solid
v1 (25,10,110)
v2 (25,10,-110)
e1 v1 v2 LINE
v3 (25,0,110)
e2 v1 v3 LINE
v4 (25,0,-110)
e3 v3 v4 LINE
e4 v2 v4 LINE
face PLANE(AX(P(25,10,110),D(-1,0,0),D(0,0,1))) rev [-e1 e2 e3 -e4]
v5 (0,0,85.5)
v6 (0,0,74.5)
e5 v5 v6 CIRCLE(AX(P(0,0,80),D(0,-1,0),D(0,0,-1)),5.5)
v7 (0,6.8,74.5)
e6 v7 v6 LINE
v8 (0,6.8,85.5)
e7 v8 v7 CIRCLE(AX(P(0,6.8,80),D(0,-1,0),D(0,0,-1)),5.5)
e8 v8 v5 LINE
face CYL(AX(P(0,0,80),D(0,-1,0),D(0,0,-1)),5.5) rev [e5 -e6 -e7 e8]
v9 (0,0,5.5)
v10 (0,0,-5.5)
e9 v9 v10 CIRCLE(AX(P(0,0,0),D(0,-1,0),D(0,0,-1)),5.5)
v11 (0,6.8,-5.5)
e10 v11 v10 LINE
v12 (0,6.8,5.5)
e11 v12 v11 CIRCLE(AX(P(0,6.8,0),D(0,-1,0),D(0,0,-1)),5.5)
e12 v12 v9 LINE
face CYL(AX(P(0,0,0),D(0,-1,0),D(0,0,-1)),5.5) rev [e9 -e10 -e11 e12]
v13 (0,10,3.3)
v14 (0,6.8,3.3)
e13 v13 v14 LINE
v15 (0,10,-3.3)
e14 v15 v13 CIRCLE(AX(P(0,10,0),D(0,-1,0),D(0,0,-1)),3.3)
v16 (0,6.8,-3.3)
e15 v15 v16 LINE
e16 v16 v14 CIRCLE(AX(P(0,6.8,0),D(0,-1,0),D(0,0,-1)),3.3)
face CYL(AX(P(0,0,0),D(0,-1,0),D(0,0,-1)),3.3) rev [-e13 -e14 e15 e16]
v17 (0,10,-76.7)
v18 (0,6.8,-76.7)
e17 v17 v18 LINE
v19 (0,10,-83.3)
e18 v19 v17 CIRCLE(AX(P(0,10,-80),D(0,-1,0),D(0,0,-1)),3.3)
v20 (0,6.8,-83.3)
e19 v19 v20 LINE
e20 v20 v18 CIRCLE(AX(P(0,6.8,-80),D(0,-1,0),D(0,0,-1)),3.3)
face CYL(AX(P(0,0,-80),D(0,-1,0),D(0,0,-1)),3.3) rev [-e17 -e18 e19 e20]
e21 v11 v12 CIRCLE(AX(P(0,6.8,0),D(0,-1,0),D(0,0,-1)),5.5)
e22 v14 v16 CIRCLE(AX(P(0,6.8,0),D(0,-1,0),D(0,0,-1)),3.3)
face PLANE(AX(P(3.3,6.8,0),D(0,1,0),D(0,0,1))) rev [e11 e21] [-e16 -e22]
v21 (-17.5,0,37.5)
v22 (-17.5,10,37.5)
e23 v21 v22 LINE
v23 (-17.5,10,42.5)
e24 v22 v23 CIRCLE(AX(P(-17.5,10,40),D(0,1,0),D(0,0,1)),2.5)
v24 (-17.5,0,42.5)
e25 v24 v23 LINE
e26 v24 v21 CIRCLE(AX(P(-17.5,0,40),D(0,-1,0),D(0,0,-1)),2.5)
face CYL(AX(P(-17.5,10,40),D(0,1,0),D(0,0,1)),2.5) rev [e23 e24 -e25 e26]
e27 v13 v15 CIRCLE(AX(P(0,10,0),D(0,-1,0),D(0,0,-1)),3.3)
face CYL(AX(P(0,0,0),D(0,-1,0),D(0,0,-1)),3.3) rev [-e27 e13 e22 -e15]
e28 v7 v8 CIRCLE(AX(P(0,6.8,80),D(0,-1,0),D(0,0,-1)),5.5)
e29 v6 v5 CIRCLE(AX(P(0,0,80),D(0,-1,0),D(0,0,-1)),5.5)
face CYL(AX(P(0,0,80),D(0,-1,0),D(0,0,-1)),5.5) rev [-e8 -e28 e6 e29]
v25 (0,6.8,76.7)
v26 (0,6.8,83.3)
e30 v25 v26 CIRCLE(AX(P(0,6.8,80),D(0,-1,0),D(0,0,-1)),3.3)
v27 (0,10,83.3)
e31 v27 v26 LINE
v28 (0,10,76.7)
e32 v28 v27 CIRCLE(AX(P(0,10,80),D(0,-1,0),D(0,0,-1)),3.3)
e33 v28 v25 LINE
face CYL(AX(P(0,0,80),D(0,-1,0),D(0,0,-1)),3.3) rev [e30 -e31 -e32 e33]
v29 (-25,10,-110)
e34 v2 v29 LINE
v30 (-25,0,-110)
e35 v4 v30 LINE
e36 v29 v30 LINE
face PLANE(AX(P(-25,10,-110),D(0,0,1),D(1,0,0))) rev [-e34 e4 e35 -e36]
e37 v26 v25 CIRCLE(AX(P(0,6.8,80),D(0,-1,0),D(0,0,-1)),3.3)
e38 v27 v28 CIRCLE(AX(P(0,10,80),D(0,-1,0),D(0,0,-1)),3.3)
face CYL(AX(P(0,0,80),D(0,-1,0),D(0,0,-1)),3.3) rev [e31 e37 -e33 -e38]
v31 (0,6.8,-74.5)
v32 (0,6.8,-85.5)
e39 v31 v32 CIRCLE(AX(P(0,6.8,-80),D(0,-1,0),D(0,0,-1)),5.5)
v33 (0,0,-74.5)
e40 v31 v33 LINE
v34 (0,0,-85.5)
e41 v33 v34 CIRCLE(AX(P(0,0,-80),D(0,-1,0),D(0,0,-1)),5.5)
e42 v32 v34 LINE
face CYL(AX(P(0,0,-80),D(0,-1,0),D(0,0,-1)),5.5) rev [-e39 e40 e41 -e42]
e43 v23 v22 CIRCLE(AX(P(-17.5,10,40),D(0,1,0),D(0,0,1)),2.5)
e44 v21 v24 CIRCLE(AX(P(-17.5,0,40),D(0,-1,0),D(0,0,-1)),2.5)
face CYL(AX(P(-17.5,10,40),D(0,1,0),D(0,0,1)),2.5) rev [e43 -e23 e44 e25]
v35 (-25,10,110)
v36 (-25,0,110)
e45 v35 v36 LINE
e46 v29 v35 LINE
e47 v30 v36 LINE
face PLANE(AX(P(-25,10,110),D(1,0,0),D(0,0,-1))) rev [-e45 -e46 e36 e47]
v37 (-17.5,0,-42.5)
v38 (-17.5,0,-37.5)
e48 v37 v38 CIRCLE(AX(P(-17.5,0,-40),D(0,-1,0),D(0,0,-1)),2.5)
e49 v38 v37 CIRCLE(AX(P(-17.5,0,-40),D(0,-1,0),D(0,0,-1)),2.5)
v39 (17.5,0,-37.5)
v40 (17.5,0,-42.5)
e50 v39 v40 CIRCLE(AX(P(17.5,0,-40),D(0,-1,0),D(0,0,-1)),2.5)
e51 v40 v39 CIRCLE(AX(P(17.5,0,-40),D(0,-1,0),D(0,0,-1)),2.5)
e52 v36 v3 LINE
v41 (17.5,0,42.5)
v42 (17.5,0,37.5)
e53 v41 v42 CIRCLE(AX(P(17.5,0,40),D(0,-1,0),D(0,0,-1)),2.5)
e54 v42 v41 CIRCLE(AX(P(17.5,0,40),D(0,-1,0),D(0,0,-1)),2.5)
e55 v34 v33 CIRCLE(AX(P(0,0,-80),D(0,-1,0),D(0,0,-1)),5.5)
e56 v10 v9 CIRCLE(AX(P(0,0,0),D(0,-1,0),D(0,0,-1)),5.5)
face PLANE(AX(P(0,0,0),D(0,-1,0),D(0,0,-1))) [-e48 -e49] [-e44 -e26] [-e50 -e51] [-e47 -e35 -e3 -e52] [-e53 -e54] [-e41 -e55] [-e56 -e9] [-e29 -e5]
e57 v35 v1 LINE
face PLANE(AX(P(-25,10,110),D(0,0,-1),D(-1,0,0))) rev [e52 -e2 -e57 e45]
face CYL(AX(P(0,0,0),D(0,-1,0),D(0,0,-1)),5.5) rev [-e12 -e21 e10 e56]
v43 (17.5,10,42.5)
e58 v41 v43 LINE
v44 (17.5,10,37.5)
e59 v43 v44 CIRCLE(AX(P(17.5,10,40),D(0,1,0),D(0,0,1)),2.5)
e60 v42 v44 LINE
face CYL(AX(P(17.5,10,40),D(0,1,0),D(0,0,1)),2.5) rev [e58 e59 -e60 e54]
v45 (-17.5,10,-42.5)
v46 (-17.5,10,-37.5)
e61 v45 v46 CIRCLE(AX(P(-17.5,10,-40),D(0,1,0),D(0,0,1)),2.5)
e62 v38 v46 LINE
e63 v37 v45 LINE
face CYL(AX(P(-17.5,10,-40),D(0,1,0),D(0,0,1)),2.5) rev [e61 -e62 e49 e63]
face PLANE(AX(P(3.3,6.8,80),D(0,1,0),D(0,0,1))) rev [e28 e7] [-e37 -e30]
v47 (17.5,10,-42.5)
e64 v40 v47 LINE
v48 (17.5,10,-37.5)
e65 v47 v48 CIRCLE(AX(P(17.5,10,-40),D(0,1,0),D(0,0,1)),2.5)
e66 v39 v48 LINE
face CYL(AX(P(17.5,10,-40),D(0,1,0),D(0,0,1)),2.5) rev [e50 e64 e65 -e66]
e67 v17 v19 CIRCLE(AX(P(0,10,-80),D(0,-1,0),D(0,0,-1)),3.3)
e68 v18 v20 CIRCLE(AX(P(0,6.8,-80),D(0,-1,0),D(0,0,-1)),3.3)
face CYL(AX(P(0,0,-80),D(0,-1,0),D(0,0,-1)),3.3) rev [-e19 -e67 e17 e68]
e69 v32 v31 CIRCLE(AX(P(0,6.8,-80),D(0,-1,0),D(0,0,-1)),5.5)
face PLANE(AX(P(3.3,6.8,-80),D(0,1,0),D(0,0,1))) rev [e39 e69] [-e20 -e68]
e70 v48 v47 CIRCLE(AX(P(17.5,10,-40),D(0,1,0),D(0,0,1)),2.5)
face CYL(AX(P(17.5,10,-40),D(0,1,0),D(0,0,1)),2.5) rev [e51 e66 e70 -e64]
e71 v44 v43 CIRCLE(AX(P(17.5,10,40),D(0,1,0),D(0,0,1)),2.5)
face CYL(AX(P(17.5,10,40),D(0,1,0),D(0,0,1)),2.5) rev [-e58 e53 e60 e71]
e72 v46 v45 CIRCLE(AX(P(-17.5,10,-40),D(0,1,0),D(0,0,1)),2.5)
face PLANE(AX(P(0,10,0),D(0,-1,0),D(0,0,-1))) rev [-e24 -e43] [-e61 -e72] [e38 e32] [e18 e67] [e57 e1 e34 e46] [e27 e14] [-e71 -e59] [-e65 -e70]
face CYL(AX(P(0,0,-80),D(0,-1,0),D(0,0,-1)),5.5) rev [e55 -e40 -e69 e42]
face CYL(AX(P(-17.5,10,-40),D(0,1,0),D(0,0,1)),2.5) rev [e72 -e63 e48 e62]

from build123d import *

# Parameters (mm, degrees)
SKETCH1_W                                         = 50
SKETCH1_H                                         = 220
BOSS_EXTRUDE1_DEPTH                               = 10
HOLE_SIZE_BY_SOCKET_HEAD_CAP_SCREW_TY_D           = 6.6
HOLE_SIZE_BY_SOCKET_HEAD_CAP_SCREW_TY_CBORE_D     = 11
HOLE_SIZE_BY_SOCKET_HEAD_CAP_SCREW_TY_CBORE_DEPTH = 6.8
M6_TAPPED_HOLE1_D                                 = 5
M6_TAPPED_HOLE1_DEPTH                             = 15
M6_TAPPED_HOLE1_TIP                               = 1.502151548


with BuildPart() as part:
    # Sketch1 → Boss-Extrude1 (new body)
    with BuildSketch(Plane(origin=(0, 0, 0), x_dir=(1, 0, 0), z_dir=(0, 1, 0))):
        Rectangle(SKETCH1_W, SKETCH1_H)
    extrude(amount=BOSS_EXTRUDE1_DEPTH)

    # Hole Size (% by) Socket Head Cap Screw Type1 (through all)
    with Locations(Plane(origin=(0, 0, 0), x_dir=(-1, 0, 0), z_dir=(0, -1, 0))):
        with Locations((0, -80), (0, 80), (0, 0)):
            CounterBoreHole(HOLE_SIZE_BY_SOCKET_HEAD_CAP_SCREW_TY_D / 2, HOLE_SIZE_BY_SOCKET_HEAD_CAP_SCREW_TY_CBORE_D / 2, HOLE_SIZE_BY_SOCKET_HEAD_CAP_SCREW_TY_CBORE_DEPTH)

    # M6 Tapped Hole1
    with Locations(Plane(origin=(0, 10, 0), x_dir=(1, 0, 0), z_dir=(0, 1, 0))):
        with Locations((-17.5, 40), (-17.5, -40), (17.5, 40), (17.5, -40)):
            Hole(M6_TAPPED_HOLE1_D / 2, depth=M6_TAPPED_HOLE1_DEPTH)
            with Locations((0, 0, -(M6_TAPPED_HOLE1_DEPTH + M6_TAPPED_HOLE1_TIP / 2))):  # 118° drill point
                Cone(0, M6_TAPPED_HOLE1_D / 2, M6_TAPPED_HOLE1_TIP, mode=Mode.SUBTRACT)


solid = part.part
